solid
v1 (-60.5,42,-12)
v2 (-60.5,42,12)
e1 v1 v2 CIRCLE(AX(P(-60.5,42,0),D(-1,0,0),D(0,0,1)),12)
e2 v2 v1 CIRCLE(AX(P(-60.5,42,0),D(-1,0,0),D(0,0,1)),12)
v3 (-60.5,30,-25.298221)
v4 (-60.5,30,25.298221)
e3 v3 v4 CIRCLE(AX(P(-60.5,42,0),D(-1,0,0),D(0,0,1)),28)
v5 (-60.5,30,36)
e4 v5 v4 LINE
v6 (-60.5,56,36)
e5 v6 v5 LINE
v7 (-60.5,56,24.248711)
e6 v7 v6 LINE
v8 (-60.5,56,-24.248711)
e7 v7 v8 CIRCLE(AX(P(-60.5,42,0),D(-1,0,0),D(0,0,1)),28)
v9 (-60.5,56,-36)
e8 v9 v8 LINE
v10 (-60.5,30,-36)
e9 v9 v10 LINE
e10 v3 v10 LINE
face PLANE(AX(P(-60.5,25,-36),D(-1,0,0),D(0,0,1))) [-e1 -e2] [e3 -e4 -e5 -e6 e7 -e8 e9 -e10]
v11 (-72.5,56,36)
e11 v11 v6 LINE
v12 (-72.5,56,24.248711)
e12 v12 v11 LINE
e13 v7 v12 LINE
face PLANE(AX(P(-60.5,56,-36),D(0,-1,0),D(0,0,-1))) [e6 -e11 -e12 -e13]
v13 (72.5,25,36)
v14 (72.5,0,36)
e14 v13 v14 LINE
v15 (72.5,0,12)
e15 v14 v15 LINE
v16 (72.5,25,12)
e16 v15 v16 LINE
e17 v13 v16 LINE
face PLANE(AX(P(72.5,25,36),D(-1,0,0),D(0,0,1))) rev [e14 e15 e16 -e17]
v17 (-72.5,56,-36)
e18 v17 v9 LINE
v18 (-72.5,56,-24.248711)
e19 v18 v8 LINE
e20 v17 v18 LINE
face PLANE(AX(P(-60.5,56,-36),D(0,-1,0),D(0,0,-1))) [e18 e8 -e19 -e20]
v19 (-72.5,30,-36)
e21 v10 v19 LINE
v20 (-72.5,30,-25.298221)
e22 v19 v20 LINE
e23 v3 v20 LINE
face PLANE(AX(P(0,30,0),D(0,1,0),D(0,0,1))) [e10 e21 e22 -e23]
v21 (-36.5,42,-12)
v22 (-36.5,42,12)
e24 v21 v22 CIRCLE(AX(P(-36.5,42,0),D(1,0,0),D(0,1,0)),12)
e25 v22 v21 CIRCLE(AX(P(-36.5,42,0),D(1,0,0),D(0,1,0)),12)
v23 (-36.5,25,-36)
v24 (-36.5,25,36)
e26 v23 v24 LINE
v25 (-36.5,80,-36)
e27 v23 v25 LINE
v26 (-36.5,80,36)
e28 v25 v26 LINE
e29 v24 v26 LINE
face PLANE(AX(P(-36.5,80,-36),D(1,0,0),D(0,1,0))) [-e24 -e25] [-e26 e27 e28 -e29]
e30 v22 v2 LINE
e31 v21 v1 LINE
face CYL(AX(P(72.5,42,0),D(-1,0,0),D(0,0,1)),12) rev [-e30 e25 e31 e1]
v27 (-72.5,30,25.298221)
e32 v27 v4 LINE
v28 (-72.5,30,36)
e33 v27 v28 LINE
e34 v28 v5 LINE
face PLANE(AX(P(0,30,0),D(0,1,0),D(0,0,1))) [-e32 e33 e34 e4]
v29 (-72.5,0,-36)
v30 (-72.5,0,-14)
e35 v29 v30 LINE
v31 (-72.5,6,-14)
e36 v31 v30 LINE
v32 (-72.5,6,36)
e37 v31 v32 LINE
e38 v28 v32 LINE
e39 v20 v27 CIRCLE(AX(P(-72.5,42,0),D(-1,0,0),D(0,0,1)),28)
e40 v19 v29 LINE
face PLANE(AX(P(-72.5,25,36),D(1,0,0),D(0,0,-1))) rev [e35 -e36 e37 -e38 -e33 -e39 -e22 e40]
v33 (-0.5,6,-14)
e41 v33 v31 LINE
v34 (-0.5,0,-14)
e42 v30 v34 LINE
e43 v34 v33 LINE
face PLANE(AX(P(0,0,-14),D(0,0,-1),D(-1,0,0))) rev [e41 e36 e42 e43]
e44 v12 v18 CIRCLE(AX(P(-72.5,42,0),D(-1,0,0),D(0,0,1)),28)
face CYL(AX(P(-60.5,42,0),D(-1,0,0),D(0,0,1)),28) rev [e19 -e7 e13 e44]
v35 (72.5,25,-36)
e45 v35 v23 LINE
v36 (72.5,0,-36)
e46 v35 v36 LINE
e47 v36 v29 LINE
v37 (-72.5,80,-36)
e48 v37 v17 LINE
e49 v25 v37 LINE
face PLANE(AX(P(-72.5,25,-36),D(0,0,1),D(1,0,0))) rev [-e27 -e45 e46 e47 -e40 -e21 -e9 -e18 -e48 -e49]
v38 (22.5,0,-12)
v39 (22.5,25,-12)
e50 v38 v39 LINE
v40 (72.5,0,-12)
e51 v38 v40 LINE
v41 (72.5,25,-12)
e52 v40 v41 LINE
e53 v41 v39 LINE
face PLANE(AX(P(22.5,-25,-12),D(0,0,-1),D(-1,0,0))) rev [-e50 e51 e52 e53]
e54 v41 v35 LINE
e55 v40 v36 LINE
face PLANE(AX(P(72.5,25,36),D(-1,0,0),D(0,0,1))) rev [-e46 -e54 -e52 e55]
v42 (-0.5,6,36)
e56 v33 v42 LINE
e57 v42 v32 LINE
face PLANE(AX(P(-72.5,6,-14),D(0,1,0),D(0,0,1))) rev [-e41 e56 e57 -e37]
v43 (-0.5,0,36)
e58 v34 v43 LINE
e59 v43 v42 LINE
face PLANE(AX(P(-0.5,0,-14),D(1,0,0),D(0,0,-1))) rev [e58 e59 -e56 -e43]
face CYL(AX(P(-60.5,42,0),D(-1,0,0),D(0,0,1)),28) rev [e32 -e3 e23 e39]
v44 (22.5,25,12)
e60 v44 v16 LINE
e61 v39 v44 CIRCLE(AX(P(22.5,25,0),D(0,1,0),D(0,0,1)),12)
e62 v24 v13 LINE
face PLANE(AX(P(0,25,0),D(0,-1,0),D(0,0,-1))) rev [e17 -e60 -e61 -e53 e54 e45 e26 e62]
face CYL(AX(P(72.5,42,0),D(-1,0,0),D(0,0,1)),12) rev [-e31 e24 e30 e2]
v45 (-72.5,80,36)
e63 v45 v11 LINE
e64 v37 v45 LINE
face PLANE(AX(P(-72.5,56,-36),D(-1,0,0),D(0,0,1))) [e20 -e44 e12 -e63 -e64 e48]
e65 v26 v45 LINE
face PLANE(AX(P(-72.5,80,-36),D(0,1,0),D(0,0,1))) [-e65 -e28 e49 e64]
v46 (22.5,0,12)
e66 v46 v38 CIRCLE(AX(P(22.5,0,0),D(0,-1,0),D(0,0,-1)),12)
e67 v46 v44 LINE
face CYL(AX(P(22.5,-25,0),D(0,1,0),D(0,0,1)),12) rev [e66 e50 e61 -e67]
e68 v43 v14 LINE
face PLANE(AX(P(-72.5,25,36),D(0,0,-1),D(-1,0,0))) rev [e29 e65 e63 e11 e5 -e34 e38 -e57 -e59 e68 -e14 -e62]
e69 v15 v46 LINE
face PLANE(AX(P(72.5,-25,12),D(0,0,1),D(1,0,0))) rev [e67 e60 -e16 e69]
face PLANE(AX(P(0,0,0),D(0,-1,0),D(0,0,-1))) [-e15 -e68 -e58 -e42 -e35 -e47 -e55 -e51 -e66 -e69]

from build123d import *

# Parameters (mm, degrees)
BASE_PLATE_SKETCH_145X72_W  = 145
BASE_PLATE_SKETCH_145X72_H  = 72
BASE_PLATE_25_THICK_DEPTH   = 25
UNDERSIDE_RELIEF_SKETCH_W   = 72
UNDERSIDE_RELIEF_SKETCH_H   = 6
UNDERSIDE_RELIEF_CUT_DEPTH  = 50
CLEVIS_SLOT_CUT_DEPTH       = 50
LOCATING_PAD_SKETCH_W       = 12
LOCATING_PAD_SKETCH_H       = 72
LOCATING_PAD_5_HIGH_DEPTH   = 5
UPRIGHT_BLOCK_72_WIDE_DEPTH = 72
COUNTERBORE_SKETCH_36_R     = 28
COUNTERBORE_36X12_DEPTH     = 12
CROSS_HOLE_SKETCH_24_R      = 12
CROSS_HOLE_24_DEPTH         = 160.32670837


with BuildPart() as part:
    # Base Plate Sketch 145x72 → Base Plate 25 Thick (new body)
    with BuildSketch(Plane(origin=(0, 0, 0), x_dir=(1, 0, 0), z_dir=(0, 1, 0))):
        Rectangle(BASE_PLATE_SKETCH_145X72_W, BASE_PLATE_SKETCH_145X72_H)
    extrude(amount=BASE_PLATE_25_THICK_DEPTH)

    # Underside Relief Sketch → Underside Relief Cut (cut)
    with BuildSketch(Plane.XY.offset(36)):
        with Locations((-36.5, 3)):
            Rectangle(UNDERSIDE_RELIEF_SKETCH_W, UNDERSIDE_RELIEF_SKETCH_H)
    extrude(amount=-UNDERSIDE_RELIEF_CUT_DEPTH, mode=Mode.SUBTRACT)

    # Clevis Slot Sketch 24 Wide → Clevis Slot Cut (cut)
    with BuildSketch(Plane(origin=(0, 25, 0), x_dir=(1, 0, 0), z_dir=(0, 1, 0))):
        with BuildLine():
            Line((22.5, 12), (72.5, 12))
            Line((72.5, 12), (72.5, -12))
            Line((72.5, -12), (22.5, -12))
            ThreePointArc((22.5, -12), (10.5, 0), (22.5, 12))
        make_face()
    extrude(amount=-CLEVIS_SLOT_CUT_DEPTH, mode=Mode.SUBTRACT)

    # Locating Pad Sketch → Locating Pad 5 High (add)
    with BuildSketch(Plane(origin=(0, 25, 0), x_dir=(1, 0, 0), z_dir=(0, 1, 0))):
        with Locations((-66.5, 0)):
            Rectangle(LOCATING_PAD_SKETCH_W, LOCATING_PAD_SKETCH_H)
    extrude(amount=LOCATING_PAD_5_HIGH_DEPTH)

    # Upright Block Profile Sketch → Upright Block 72 Wide (add)
    with BuildSketch(Plane.XY.offset(36)):
        Polygon((-60.5, 25), (-60.5, 56), (-72.5, 56), (-72.5, 80), (-36.5, 80), (-36.5, 25), align=None)
    extrude(amount=-UPRIGHT_BLOCK_72_WIDE_DEPTH)

    # Counterbore Sketch Ø36 → Counterbore Ø36x12 (cut)
    with BuildSketch(Plane.ZY.offset(72.5)):
        with Locations((0, 42)):
            Circle(COUNTERBORE_SKETCH_36_R)
    extrude(amount=-COUNTERBORE_36X12_DEPTH, mode=Mode.SUBTRACT)

    # Cross Hole Sketch Ø24 → Cross Hole Ø24 (cut, through all)
    with BuildSketch(Plane.ZY.offset(60.5)):
        with Locations((0, 42)):
            Circle(CROSS_HOLE_SKETCH_24_R)
    extrude(amount=-CROSS_HOLE_24_DEPTH, mode=Mode.SUBTRACT)


solid = part.part
